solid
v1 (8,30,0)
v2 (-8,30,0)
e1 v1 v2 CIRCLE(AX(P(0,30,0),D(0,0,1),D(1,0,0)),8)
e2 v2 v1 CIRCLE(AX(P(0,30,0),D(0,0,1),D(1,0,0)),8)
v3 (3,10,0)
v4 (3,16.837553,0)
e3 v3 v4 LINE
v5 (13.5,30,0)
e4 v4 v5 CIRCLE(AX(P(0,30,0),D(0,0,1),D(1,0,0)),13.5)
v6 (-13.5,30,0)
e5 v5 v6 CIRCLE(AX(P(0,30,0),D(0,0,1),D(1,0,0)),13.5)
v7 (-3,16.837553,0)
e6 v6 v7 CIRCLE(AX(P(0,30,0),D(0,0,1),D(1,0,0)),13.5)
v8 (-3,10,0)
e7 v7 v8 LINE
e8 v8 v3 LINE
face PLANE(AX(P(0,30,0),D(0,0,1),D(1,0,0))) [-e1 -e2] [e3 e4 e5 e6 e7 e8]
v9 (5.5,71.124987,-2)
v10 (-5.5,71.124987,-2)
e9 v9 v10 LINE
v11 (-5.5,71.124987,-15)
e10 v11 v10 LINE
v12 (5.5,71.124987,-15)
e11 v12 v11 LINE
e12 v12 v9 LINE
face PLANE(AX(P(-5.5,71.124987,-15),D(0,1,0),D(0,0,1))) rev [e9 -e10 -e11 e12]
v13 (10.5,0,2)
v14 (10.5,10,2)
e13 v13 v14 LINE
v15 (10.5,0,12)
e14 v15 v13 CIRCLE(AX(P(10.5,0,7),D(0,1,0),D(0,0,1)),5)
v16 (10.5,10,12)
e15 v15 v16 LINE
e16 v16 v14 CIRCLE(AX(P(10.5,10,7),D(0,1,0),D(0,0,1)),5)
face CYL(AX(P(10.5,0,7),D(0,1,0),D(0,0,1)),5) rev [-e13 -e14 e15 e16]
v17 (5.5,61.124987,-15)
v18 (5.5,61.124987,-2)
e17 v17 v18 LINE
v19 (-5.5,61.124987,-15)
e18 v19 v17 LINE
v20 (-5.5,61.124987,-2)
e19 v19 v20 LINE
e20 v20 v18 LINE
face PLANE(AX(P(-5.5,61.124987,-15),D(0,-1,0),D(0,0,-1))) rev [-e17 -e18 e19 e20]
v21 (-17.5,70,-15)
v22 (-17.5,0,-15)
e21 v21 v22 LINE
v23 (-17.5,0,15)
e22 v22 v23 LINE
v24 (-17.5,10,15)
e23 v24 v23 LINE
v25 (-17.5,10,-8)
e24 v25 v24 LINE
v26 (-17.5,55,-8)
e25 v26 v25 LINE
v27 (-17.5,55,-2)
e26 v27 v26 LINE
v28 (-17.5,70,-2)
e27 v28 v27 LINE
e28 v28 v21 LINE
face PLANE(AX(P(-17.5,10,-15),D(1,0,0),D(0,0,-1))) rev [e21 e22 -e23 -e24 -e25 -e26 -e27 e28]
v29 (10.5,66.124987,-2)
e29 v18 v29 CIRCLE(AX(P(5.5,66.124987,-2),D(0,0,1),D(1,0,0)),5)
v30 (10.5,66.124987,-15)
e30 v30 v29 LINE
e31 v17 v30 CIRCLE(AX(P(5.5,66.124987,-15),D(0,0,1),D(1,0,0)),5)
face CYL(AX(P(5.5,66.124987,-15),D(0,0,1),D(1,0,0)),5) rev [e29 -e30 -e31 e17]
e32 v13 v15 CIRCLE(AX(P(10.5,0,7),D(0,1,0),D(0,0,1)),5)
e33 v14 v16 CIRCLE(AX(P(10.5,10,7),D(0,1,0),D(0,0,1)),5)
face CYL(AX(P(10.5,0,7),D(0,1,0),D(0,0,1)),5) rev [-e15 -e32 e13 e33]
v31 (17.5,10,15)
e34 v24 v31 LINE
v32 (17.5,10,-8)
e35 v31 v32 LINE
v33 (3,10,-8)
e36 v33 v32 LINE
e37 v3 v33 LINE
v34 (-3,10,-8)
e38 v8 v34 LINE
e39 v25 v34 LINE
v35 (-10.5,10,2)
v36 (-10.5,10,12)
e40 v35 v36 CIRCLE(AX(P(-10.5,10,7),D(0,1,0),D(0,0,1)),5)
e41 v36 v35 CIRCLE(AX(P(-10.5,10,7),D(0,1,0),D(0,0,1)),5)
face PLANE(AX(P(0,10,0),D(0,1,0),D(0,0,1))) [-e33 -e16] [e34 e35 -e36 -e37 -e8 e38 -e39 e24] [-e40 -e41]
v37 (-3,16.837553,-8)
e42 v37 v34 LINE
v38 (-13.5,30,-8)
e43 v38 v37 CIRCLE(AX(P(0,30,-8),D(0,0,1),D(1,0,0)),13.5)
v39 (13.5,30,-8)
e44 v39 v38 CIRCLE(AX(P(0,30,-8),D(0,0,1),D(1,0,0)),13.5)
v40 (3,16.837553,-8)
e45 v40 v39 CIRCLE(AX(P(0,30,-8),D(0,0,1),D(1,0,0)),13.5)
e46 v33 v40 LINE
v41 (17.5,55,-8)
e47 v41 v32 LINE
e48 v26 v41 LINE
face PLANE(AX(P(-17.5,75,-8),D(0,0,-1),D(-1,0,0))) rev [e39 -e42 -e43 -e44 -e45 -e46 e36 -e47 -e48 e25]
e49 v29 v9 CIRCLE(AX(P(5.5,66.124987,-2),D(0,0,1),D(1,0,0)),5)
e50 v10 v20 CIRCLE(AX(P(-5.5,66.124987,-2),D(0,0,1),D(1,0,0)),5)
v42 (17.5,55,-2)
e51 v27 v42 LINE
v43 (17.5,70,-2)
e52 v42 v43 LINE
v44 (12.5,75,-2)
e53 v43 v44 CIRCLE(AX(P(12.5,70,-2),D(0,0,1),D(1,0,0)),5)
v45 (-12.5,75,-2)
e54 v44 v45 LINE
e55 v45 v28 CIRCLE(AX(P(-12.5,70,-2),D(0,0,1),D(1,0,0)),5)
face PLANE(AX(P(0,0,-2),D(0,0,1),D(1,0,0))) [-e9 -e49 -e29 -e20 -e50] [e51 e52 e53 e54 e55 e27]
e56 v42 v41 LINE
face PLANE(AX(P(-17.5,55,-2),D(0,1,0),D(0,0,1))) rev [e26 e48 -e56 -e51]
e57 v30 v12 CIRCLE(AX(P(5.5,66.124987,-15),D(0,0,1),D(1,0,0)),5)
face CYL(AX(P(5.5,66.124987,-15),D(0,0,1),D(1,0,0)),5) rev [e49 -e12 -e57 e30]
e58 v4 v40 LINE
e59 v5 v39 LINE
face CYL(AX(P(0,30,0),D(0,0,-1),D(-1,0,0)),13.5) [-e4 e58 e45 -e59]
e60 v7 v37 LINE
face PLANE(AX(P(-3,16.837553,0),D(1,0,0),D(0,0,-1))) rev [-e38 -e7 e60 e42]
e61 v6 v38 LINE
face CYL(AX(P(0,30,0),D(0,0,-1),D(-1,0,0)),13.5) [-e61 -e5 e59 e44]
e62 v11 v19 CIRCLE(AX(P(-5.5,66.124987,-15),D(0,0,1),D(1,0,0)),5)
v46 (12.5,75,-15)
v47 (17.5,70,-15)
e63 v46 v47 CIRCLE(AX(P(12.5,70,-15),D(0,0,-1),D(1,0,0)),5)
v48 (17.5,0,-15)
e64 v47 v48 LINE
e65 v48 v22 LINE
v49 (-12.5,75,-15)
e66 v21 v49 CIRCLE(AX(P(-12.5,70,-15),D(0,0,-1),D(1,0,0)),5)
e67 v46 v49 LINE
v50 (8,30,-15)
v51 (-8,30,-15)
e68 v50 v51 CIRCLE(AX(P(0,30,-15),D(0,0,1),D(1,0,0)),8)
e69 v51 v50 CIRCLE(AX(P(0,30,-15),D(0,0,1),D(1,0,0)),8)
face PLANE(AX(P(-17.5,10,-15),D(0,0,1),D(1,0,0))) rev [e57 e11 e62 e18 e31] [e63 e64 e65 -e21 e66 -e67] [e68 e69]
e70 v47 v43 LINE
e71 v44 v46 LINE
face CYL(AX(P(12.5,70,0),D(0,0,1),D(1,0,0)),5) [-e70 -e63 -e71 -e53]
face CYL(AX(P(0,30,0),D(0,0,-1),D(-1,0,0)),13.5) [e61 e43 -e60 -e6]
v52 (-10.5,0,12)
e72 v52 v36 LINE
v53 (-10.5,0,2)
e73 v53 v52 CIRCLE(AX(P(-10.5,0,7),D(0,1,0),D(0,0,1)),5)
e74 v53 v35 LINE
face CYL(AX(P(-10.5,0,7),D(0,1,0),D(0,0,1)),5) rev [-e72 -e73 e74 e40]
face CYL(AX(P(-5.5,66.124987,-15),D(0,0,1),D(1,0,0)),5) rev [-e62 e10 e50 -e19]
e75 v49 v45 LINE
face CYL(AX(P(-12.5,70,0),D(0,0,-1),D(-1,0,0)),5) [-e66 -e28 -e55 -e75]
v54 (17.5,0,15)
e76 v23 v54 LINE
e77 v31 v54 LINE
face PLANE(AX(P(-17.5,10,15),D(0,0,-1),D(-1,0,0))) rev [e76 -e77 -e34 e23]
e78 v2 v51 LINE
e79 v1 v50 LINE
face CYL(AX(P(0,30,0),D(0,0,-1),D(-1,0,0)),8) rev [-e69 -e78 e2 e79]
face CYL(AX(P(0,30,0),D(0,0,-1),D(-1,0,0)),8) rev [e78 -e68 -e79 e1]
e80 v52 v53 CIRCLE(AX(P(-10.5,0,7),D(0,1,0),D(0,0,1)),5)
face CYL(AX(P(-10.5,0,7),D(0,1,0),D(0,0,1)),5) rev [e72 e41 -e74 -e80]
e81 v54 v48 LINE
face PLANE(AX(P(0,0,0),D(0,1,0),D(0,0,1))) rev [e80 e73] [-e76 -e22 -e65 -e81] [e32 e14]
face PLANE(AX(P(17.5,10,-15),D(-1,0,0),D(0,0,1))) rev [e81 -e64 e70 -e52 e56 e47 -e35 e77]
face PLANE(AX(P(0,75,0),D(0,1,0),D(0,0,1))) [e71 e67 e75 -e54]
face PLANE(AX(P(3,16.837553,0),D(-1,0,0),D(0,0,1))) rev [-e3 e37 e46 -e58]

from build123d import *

# Parameters (mm, degrees)
BASE_PLATE_SKETCH_W      = 35
BASE_PLATE_SKETCH_H      = 30
BASE_PLATE_DEPTH         = 10
UPRIGHT_WALL_SKETCH_W    = 35
UPRIGHT_WALL_SKETCH_H    = 7
UPRIGHT_WALL_DEPTH       = 65
TOP_PAD_SKETCH_W         = 35
TOP_PAD_SKETCH_H         = 20
TOP_PAD_DEPTH            = 6
WALL_MOUNTING_SLOT_DEPTH = 13
BEARING_BOSS_SKETCH_R    = 8
BEARING_BOSS_DEPTH       = 8
BASE_HOLE_A_SKETCH_R     = 5
BASE_HOLE_A_DEPTH        = 10
BASE_HOLE_B_SKETCH_R     = 5
BASE_HOLE_B_DEPTH        = 10
BEARING_START            = -10
BEARING_BORE_SKETCH_R    = 8
BEARING_BORE_DEPTH       = 10
WALL_TOP_FILLET_R5_A_R   = 5
WALL_TOP_FILLET_R5_B_R   = 5


with BuildPart() as part:
    # Base Plate Sketch → Base Plate (new body)
    with BuildSketch(Plane(origin=(0, 0, 0), x_dir=(1, 0, 0), z_dir=(0, 1, 0))):
        Rectangle(BASE_PLATE_SKETCH_W, BASE_PLATE_SKETCH_H)
    extrude(amount=BASE_PLATE_DEPTH)

    # Upright Wall Sketch → Upright Wall (add)
    with BuildSketch(Plane(origin=(0, 10, 0), x_dir=(1, 0, 0), z_dir=(0, 1, 0))):
        with Locations((0, 11.5)):
            Rectangle(UPRIGHT_WALL_SKETCH_W, UPRIGHT_WALL_SKETCH_H)
    extrude(amount=UPRIGHT_WALL_DEPTH)

    # Top Pad Sketch → Top Pad (add)
    with BuildSketch(Plane.XY.offset(-8)):
        with Locations((0, 65)):
            Rectangle(TOP_PAD_SKETCH_W, TOP_PAD_SKETCH_H)
    extrude(amount=TOP_PAD_DEPTH)

    # Wall Mounting Slot Sketch → Wall Mounting Slot (cut)
    with BuildSketch(Plane.XY.offset(-2)):
        with BuildLine():
            Line((-5.5, 71.124987094), (5.5, 71.124987094))
            ThreePointArc((5.5, 71.124987094), (10.5, 66.124987094), (5.5, 61.124987094))
            Line((5.5, 61.124987094), (-5.5, 61.124987094))
            ThreePointArc((-5.5, 61.124987094), (-10.5, 66.124987094), (-5.5, 71.124987094))
        make_face()
    extrude(amount=-WALL_MOUNTING_SLOT_DEPTH, mode=Mode.SUBTRACT)

    # Bearing Boss Sketch → Bearing Boss (add)
    with BuildSketch(Plane.XY.offset(-8)):
        with BuildLine():
            Line((-3, 16.837553419), (-3, 10))
            Line((-3, 10), (3, 10))
            Line((3, 10), (3, 16.837553419))
            ThreePointArc((3, 16.837553419), (0, 43.5), (-3, 16.837553419))
        make_face()
        with Locations((0, 30)):
            Circle(BEARING_BOSS_SKETCH_R, mode=Mode.SUBTRACT)
    extrude(amount=BEARING_BOSS_DEPTH)

    # Base Hole A Sketch → Base Hole A (cut)
    with BuildSketch(Plane(origin=(0, 10, 0), x_dir=(1, 0, 0), z_dir=(0, 1, 0))):
        with Locations(Location((-10.5, -7, 0), (0, 0, 270))):
            Circle(BASE_HOLE_A_SKETCH_R)
    extrude(amount=-BASE_HOLE_A_DEPTH, mode=Mode.SUBTRACT)

    # Base Hole B Sketch → Base Hole B (cut)
    with BuildSketch(Plane(origin=(0, 10, 0), x_dir=(1, 0, 0), z_dir=(0, 1, 0))):
        with Locations(Location((10.5, -7, 0), (0, 0, 270))):
            Circle(BASE_HOLE_B_SKETCH_R)
    extrude(amount=-BASE_HOLE_B_DEPTH, mode=Mode.SUBTRACT)

    # Bearing Bore Sketch → Bearing Bore (cut)
    with BuildSketch(Plane.XY.offset(-8).offset(BEARING_START)):
        with Locations((0, 30)):
            Circle(BEARING_BORE_SKETCH_R)
    extrude(amount=BEARING_BORE_DEPTH, mode=Mode.SUBTRACT)

    # Wall Top Fillet R5 A
    wall_top_fillet_r5_a_edges = [part.edges().sort_by_distance(p)[0] for p in [
        (-17.5, 75, -8.5),
    ]]
    fillet(wall_top_fillet_r5_a_edges, radius=WALL_TOP_FILLET_R5_A_R)

    # Wall Top Fillet R5 B
    wall_top_fillet_r5_b_edges = [part.edges().sort_by_distance(p)[0] for p in [
        (17.5, 75, -8.5),
    ]]
    fillet(wall_top_fillet_r5_b_edges, radius=WALL_TOP_FILLET_R5_B_R)


solid = part.part
